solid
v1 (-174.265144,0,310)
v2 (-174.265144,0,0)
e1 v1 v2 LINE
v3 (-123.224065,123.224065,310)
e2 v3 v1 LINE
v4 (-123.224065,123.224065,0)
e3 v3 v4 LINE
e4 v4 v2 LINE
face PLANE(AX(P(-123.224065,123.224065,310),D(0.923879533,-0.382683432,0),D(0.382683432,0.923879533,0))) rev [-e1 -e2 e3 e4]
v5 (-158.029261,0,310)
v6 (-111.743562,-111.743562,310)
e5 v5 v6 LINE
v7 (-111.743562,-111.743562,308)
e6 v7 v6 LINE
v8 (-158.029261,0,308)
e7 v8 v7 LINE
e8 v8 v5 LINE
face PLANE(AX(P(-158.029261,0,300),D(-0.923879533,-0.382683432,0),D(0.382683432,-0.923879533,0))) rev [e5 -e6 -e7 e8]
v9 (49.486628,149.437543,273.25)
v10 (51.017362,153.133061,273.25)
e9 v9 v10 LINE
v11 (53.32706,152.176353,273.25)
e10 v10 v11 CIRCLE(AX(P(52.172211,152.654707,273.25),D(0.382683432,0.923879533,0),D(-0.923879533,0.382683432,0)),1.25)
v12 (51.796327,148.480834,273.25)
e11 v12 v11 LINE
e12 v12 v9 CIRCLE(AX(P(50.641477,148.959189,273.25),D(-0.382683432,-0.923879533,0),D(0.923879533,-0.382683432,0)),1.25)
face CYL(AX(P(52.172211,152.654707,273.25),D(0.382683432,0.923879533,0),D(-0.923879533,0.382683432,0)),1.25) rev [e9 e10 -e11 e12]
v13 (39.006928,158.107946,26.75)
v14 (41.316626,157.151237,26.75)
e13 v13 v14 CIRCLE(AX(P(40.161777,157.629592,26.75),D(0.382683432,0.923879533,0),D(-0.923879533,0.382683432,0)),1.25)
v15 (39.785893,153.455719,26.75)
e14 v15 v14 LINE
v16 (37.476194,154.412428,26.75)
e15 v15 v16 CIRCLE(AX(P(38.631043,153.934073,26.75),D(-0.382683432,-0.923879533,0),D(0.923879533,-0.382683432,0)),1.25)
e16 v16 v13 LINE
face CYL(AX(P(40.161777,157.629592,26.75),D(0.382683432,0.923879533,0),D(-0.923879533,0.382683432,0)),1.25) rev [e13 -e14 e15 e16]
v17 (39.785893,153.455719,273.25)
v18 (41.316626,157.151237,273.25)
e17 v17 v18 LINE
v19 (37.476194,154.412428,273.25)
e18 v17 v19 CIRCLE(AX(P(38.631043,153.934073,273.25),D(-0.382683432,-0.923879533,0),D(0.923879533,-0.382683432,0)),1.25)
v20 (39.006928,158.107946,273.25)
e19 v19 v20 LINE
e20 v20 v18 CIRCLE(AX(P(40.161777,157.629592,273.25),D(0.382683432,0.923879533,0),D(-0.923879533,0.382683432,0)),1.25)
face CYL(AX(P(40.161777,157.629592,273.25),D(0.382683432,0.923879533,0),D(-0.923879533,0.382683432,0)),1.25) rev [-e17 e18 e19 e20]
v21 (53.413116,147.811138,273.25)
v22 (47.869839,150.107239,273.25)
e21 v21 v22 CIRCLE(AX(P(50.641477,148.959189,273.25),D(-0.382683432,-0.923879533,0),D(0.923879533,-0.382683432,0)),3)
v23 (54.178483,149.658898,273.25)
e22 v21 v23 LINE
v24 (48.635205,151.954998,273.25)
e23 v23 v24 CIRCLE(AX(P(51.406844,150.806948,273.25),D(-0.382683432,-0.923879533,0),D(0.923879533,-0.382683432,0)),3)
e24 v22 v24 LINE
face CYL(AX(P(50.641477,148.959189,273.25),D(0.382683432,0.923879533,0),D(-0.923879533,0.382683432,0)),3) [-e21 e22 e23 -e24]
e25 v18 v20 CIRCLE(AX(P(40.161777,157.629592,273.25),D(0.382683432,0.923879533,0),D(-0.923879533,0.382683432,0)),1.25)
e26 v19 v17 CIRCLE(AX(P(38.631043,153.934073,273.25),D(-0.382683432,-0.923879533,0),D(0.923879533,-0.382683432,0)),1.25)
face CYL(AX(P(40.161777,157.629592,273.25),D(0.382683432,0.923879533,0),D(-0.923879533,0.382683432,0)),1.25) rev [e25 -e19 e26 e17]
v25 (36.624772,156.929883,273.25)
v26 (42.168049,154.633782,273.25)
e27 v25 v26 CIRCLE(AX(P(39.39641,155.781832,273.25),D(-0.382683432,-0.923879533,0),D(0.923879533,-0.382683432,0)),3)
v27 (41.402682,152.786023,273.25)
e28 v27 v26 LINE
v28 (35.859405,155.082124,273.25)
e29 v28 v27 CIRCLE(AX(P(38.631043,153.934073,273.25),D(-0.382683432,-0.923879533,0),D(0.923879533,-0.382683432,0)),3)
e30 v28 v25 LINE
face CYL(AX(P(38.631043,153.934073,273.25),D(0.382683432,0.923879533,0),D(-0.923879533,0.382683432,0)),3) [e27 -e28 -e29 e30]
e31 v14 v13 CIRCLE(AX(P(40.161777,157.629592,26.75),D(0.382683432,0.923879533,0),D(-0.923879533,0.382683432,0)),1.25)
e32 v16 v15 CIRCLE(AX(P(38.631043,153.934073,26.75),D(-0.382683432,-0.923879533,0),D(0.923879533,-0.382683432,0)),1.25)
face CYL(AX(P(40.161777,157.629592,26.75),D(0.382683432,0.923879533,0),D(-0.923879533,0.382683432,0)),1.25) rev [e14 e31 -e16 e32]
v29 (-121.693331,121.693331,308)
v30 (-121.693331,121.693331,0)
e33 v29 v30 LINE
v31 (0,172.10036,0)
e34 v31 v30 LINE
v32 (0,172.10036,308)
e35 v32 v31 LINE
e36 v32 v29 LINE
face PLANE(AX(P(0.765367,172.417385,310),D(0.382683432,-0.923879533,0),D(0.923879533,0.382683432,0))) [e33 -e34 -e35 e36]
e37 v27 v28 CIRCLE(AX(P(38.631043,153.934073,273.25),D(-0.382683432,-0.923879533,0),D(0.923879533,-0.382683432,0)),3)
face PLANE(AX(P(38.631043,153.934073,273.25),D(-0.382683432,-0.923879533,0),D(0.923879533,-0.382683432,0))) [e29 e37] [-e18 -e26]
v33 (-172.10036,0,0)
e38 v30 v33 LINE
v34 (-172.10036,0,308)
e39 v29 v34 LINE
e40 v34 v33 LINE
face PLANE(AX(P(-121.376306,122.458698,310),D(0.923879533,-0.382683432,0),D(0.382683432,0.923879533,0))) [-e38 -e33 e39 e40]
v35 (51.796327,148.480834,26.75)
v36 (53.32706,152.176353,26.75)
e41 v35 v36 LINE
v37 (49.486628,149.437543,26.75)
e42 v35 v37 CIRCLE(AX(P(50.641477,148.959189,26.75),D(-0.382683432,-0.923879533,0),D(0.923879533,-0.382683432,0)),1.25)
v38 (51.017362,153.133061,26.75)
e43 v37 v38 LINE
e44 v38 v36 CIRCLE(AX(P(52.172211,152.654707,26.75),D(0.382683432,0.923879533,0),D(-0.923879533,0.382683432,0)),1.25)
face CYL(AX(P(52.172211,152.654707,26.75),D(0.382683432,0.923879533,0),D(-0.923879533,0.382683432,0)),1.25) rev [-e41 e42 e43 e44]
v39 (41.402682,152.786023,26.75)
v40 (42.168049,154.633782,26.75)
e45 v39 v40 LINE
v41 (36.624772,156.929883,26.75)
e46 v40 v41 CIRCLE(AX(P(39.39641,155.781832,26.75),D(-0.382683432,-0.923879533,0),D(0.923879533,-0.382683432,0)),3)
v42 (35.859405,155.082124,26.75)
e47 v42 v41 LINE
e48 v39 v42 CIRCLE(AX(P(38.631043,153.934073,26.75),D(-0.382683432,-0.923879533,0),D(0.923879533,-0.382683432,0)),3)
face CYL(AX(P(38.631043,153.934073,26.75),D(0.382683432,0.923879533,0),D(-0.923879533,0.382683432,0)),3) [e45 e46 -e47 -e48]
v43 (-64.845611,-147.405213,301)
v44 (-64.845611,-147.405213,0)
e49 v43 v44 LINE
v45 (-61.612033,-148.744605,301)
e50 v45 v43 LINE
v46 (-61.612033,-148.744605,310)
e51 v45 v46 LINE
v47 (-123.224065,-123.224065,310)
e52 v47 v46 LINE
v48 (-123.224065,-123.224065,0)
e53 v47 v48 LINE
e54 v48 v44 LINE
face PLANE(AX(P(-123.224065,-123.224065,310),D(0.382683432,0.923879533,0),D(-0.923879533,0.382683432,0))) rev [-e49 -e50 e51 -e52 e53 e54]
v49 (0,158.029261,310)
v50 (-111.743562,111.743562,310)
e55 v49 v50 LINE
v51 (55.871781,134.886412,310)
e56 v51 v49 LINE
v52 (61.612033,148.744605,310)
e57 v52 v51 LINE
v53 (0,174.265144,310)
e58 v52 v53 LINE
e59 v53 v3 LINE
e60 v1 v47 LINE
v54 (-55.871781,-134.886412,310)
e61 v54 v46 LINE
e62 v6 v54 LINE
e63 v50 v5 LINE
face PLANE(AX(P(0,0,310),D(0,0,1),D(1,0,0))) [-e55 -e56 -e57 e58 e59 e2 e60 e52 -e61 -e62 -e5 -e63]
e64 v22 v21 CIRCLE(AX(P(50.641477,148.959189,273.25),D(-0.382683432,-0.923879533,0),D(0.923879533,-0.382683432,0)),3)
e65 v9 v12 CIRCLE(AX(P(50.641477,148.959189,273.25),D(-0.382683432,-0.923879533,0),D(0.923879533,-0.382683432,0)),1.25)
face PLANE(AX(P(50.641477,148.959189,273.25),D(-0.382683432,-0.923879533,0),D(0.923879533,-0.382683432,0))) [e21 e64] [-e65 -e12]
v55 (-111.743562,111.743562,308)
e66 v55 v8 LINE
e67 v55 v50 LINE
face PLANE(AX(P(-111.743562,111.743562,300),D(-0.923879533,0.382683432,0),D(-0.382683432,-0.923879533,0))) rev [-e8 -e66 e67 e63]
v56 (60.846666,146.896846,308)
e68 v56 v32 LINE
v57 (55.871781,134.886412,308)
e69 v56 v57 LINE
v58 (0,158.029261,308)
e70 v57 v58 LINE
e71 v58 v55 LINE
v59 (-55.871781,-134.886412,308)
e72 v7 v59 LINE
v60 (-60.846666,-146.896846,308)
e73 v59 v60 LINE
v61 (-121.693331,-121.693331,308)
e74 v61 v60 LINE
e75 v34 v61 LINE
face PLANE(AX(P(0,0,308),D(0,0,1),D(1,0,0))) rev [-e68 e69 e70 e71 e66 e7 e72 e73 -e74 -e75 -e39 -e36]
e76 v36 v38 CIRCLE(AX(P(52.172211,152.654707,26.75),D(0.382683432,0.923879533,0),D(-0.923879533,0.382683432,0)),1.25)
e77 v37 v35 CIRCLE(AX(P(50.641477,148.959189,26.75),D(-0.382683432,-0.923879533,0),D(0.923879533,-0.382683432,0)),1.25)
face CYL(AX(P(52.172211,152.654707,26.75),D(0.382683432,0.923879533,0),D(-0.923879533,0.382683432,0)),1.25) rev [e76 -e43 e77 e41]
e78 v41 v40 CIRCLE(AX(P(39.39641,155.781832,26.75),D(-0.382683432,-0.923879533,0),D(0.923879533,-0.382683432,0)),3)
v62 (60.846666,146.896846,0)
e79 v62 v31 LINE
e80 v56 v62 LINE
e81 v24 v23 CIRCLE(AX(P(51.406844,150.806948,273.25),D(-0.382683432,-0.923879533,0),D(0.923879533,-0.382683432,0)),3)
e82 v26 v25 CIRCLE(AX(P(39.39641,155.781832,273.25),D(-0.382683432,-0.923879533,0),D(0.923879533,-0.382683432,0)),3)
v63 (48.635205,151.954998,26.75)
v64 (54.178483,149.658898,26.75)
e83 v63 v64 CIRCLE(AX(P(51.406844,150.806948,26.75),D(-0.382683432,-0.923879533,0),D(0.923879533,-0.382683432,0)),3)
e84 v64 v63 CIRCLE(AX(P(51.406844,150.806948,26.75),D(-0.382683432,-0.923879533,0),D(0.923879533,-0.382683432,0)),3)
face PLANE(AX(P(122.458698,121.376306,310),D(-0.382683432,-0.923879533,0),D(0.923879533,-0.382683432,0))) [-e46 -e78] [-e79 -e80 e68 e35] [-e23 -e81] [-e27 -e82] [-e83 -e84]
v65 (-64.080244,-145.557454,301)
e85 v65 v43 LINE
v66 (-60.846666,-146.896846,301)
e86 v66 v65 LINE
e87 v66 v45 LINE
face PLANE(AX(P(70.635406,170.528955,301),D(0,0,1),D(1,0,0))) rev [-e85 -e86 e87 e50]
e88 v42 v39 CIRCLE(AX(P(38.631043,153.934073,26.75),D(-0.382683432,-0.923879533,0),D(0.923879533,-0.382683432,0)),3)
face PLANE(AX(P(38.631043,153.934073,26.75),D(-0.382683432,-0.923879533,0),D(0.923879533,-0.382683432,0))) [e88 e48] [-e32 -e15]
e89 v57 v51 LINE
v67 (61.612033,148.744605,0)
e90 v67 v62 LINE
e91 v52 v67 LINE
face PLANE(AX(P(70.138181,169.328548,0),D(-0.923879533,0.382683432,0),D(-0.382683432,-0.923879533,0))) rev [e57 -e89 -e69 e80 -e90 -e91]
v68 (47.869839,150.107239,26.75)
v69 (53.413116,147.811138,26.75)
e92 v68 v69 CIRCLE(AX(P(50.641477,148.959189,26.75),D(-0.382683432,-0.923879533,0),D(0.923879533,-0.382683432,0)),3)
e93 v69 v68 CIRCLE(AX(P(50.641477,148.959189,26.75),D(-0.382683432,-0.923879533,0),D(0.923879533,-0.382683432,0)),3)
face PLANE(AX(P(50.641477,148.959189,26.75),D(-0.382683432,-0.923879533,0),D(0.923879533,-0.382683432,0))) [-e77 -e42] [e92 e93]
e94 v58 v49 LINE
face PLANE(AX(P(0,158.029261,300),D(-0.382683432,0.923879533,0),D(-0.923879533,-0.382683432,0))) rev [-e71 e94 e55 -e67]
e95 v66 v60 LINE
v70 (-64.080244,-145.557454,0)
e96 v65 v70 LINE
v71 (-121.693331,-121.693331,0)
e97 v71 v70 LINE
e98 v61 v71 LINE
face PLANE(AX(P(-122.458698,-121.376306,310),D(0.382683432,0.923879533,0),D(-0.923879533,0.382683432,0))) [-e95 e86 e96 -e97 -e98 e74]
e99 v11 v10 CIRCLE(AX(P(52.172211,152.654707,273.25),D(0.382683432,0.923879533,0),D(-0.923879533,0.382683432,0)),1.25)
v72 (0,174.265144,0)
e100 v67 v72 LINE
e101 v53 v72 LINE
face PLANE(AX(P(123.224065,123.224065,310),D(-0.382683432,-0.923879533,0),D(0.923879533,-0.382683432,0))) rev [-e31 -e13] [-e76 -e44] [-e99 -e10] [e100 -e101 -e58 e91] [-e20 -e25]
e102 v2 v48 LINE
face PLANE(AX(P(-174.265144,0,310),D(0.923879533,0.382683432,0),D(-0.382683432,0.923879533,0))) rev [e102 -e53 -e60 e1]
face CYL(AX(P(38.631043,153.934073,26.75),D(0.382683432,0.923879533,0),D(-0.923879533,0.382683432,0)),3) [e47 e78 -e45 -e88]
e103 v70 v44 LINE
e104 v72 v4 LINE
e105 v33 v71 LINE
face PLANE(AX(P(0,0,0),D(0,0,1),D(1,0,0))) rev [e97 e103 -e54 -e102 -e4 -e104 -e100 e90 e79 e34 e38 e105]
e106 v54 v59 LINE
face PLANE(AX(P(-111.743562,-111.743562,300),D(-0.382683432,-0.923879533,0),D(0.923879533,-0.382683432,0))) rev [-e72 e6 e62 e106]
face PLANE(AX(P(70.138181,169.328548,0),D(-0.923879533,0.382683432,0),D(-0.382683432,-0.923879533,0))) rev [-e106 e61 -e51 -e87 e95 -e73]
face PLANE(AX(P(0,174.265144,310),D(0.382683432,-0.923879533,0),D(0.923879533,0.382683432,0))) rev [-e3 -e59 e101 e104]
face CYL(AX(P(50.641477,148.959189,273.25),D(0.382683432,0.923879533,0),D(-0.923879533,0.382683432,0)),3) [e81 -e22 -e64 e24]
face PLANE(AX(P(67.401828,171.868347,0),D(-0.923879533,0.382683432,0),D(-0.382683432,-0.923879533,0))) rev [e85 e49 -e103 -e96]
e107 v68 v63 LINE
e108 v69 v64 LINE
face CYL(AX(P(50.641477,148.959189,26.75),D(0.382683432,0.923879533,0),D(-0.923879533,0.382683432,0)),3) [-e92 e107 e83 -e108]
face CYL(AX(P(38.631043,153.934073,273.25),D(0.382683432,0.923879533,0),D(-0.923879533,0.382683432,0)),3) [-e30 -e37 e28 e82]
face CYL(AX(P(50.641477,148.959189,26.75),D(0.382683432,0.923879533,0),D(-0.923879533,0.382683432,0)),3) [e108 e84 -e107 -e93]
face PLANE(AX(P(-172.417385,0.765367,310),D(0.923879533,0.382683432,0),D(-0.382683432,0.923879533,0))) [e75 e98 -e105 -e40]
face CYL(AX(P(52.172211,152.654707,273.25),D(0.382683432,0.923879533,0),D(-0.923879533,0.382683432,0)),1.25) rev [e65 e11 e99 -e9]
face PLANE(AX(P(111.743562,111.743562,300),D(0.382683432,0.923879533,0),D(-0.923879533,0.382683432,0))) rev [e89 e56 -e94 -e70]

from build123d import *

# Parameters (mm, degrees)
BOSS_EXTRUDE1_DEPTH   = 310
SHELL1_T              = -2
CUT_EXTRUDE1_DEPTH    = 10
CUT_EXTRUDE2_DEPTH    = 397.026111511
SKETCH4_R             = 3
BOSS_EXTRUDE2_DEPTH   = 2
M3_TAPPED_HOLE1_D     = 2.5
M3_TAPPED_HOLE1_DEPTH = 4
CUT_EXTRUDE3_REACH    = 466.348
SKETCH7_W             = 3.5
SKETCH7_H             = 301


with BuildPart() as part:
    # Sketch1 → Boss-Extrude1 (new body)
    with BuildSketch(Plane.XY):
        Polygon((-174.265144247, 0), (-123.224065222, -123.224065222), (0, -174.265144247), (123.224065222, -123.224065222), (174.265144247, 0), (123.224065222, 123.224065222), (0, 174.265144247), (-123.224065222, 123.224065222), align=None)
    extrude(amount=BOSS_EXTRUDE1_DEPTH)

    # Shell1
    shell1_openings = [part.faces().sort_by_distance(p)[0] for p in [
        (0, 0, 0),
    ]]
    offset(amount=SHELL1_T, openings=shell1_openings, kind=Kind.INTERSECTION)

    # Sketch2 → Cut-Extrude1 (cut)
    with BuildSketch(Plane.XY.offset(310)):
        Polygon((111.743562251, 111.743562251), (0, 158.029261243), (-111.743562251, 111.743562251), (-158.029261243, 0), (-111.743562251, -111.743562251), (0, -158.029261243), (111.743562251, -111.743562251), (158.029261243, 0), align=None)
    extrude(amount=-CUT_EXTRUDE1_DEPTH, mode=Mode.SUBTRACT)

    # Sketch3 → Cut-Extrude2 (cut, through all)
    with BuildSketch(Plane.XY.offset(310)):
        Polygon((70.138181093, 169.328548035), (-63.801020235, -154.029288344), (130.028007017, -234.315900213), (263.967208344, 89.041936166), align=None)
    extrude(amount=-CUT_EXTRUDE2_DEPTH, mode=Mode.SUBTRACT)

    # Sketch4 → Boss-Extrude2 (add)
    with BuildSketch(Plane(origin=(60.846665746, 146.896845669, 0), x_dir=(0.9238795325112958, -0.38268343236506785, 0), z_dir=(-0.38268343236506785, -0.9238795325112958, 0))):
        with Locations((-23.217589358, 273.25)):
            Circle(SKETCH4_R)
        with Locations((-10.217589358, 273.25)):
            Circle(SKETCH4_R)
        with Locations((-10.217589358, 26.75)):
            Circle(SKETCH4_R)
        with Locations((-23.217589358, 26.75)):
            Circle(SKETCH4_R)
    extrude(amount=BOSS_EXTRUDE2_DEPTH)

    # M3 Tapped Hole1
    with Locations(Plane(origin=(61.612032611, 148.744604734, 0), x_dir=(0.9238795325112958, -0.38268343236506785, 0), z_dir=(0.38268343236506785, 0.9238795325112958, 0))):
        with Locations((-23.217589358, -26.75), (-10.217589358, -26.75), (-23.217589358, -273.25), (-10.217589358, -273.25)):
            Hole(M3_TAPPED_HOLE1_D / 2, depth=M3_TAPPED_HOLE1_DEPTH)

    # Sketch7 → Cut-Extrude3 (cut, up to next)
    with BuildSketch(Plane(origin=(-61.612032611, -148.744604734, 0), x_dir=(0.9238795325112957, -0.38268343236506797, 0), z_dir=(-0.38268343236506797, -0.9238795325112957, 0)), mode=Mode.PRIVATE) as cut_extrude3_sk1:
        with Locations((-1.75, 150.5)):
            Rectangle(SKETCH7_W, SKETCH7_H)
    cut_extrude3_tool1 = extrude(cut_extrude3_sk1.sketch, amount=-CUT_EXTRUDE3_REACH, mode=Mode.PRIVATE) & part.part
    add(cut_extrude3_tool1.solids().sort_by_distance((-63.228822, -148.074909, 150.5))[0], mode=Mode.SUBTRACT)


solid = part.part
